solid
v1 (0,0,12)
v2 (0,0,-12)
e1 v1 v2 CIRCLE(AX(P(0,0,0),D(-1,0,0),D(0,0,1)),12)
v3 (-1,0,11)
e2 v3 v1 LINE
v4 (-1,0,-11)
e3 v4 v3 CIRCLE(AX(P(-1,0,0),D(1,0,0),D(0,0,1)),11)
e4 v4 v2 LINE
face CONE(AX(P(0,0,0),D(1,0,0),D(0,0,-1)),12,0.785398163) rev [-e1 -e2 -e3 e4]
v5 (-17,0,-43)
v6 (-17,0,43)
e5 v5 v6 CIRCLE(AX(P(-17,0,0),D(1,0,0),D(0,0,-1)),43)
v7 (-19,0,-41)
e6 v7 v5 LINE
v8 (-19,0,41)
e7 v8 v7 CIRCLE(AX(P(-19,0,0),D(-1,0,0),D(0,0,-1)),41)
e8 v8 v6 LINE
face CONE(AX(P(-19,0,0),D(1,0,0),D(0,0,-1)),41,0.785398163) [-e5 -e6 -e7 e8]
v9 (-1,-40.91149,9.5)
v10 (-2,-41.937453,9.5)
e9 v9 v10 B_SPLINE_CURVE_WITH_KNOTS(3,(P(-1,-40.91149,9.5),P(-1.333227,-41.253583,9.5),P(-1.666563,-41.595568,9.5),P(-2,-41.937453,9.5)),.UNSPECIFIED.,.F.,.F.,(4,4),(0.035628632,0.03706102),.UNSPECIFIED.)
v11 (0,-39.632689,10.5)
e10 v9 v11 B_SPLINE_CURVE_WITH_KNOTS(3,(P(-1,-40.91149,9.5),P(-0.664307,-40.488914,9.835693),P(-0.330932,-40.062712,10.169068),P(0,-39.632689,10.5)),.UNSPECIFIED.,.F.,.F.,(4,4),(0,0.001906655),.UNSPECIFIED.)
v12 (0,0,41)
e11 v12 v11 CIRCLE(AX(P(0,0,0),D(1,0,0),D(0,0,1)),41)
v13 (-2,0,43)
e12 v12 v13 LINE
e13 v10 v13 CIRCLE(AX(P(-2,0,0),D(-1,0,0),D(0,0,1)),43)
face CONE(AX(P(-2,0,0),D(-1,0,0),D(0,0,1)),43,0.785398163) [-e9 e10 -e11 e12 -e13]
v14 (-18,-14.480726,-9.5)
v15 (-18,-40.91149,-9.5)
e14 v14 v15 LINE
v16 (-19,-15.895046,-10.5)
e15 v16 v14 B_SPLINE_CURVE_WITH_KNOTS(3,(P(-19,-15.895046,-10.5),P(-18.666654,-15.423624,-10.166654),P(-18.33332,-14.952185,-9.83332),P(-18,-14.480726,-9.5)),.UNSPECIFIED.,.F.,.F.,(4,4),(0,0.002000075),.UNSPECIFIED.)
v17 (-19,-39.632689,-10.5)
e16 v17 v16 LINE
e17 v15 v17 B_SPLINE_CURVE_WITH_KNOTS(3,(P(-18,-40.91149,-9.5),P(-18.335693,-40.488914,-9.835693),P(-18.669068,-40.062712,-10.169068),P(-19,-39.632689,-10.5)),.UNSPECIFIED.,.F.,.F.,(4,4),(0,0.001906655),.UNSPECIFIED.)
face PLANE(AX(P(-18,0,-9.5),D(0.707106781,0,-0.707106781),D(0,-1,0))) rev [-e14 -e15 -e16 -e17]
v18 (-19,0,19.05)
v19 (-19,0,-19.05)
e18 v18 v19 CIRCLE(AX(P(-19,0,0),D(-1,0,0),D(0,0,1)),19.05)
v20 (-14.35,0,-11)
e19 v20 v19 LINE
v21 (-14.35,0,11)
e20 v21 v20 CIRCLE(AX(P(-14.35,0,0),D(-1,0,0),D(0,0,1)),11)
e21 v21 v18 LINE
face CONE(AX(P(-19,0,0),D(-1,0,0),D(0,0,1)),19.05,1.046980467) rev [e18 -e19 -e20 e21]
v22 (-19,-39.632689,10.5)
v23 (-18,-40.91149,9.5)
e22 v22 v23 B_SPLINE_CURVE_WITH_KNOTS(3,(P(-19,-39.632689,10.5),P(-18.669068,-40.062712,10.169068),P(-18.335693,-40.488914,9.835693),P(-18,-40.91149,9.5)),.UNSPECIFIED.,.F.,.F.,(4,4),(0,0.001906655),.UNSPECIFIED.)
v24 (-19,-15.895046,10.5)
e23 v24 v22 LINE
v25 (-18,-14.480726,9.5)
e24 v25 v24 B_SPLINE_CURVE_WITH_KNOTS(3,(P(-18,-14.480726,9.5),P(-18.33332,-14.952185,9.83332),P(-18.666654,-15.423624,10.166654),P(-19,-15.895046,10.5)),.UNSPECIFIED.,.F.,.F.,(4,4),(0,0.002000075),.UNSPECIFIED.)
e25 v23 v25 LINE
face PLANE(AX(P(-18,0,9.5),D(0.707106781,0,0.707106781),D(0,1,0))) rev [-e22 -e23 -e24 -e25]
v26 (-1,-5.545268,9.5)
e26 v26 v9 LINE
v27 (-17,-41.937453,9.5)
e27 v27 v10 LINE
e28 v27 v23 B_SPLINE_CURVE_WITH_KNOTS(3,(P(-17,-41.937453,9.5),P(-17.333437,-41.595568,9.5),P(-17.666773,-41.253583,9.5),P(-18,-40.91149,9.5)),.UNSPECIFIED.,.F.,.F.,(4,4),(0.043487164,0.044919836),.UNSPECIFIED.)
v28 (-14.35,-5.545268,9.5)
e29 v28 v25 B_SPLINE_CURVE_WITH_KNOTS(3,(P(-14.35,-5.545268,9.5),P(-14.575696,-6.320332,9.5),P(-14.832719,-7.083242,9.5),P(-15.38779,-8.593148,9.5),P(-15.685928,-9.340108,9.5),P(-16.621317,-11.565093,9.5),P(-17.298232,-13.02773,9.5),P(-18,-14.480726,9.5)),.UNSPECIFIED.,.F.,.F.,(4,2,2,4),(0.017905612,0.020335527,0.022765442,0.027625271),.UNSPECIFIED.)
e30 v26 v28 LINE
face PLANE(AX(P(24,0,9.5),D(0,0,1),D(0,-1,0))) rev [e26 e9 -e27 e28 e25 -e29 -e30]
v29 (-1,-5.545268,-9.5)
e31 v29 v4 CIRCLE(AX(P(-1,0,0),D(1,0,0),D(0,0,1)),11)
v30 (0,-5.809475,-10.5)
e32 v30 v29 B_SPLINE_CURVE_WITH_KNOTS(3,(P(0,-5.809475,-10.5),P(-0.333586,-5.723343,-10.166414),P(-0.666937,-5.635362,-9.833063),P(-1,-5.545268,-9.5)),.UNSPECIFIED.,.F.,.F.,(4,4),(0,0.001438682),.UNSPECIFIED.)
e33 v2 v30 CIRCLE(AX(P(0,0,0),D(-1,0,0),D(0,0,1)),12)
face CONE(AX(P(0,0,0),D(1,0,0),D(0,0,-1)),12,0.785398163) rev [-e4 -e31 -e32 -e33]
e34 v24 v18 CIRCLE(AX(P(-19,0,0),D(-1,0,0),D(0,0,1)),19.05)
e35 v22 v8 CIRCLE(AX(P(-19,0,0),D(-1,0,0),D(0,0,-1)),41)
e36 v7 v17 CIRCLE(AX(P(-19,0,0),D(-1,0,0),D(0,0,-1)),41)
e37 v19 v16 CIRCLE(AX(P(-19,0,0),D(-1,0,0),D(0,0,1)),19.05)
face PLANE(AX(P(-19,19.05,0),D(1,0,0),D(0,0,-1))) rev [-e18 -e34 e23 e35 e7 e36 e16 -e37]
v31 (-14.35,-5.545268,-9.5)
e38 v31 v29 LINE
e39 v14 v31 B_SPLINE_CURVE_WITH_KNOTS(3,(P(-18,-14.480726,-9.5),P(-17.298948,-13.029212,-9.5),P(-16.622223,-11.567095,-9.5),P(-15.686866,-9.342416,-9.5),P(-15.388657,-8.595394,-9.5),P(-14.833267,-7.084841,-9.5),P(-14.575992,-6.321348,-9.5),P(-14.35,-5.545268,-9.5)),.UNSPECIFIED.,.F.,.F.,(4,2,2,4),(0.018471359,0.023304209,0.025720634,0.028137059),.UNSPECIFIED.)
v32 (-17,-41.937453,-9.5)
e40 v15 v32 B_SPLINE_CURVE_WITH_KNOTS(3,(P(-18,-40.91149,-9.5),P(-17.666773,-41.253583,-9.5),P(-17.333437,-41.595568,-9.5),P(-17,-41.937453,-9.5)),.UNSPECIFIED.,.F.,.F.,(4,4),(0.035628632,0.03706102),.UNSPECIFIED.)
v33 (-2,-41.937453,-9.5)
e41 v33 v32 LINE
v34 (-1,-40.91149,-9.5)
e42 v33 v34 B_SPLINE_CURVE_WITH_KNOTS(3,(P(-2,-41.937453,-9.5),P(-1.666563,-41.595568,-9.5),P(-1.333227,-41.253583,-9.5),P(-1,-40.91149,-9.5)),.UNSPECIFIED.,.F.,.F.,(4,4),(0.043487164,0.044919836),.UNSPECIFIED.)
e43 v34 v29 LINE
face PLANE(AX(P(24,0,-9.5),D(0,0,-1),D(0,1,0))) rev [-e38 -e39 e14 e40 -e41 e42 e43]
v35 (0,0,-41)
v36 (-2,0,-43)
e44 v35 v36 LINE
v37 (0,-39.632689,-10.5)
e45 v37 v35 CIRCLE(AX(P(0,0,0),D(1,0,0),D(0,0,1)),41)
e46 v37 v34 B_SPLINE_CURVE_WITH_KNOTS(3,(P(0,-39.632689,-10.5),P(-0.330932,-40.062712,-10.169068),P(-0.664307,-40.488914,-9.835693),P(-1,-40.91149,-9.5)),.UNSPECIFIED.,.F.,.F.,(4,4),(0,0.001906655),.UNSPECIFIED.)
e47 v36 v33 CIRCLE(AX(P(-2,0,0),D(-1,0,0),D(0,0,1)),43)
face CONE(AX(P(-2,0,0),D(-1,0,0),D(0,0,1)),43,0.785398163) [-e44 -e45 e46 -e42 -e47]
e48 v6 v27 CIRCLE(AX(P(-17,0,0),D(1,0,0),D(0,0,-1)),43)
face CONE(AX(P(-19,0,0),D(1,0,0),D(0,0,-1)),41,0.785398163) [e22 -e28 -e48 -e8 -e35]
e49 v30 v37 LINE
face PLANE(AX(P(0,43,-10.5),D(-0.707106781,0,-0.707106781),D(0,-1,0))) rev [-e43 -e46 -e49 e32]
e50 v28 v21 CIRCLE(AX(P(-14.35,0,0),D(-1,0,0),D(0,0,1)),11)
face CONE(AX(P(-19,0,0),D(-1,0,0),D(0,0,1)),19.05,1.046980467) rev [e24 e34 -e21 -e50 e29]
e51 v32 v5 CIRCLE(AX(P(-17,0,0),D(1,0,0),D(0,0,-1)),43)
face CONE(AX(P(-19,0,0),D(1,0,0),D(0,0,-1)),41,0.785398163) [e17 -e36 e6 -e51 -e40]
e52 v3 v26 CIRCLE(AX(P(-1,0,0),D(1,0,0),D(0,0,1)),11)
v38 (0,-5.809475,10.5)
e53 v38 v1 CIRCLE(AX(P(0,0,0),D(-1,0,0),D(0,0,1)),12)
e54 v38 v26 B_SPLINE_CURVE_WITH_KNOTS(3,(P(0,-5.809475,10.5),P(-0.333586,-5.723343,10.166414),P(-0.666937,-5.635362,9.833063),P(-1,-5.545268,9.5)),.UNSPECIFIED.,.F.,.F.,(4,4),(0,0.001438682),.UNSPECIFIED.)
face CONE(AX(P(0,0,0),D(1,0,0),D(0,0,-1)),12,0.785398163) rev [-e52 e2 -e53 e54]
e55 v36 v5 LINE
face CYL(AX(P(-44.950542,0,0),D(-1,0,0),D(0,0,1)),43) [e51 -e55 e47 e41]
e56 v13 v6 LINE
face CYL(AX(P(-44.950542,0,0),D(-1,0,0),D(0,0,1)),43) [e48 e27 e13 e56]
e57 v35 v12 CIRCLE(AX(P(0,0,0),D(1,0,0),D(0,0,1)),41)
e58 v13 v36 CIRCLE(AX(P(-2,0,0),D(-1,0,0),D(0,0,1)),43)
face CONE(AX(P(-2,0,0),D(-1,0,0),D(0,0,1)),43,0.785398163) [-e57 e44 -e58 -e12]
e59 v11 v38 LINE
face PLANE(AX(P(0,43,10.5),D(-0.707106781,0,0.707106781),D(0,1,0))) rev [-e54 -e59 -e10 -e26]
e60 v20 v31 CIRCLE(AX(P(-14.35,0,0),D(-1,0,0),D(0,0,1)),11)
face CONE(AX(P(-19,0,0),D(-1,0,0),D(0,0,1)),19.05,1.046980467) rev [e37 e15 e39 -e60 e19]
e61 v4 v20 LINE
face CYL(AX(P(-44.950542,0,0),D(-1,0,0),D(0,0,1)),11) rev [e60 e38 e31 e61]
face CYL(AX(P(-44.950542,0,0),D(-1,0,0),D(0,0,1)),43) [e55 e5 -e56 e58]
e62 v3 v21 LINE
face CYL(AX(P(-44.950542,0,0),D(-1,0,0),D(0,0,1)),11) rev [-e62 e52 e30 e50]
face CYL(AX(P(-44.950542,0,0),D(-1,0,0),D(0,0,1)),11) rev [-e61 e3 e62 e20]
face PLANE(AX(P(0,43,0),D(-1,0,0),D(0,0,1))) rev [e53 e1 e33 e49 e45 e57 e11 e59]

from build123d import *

# Parameters (mm, degrees)
CHAMFER1_SIZE      = 2
CUT_EXTRUDE2_DEPTH = 43
CHAMFER2_SIZE      = 1


with BuildPart() as part:
    # Sketch1 → Revolve1 (revolve)
    with BuildSketch(Plane.XY, mode=Mode.PRIVATE) as revolve1_sk:
        Polygon((-19, 19.05), (-19, 43), (0, 43), (0, 11), (-14.35, 11), align=None)
    revolve(revolve1_sk.sketch.rotate(Axis((-44.950542037, 0, 0), (1, 0, 0)), 90), axis=Axis((-44.950542037, 0, 0), (1, 0, 0)))

    # Chamfer1
    chamfer1_edges = [part.edges().sort_by_distance(p)[0] for p in [
        (-19, 0, -43),
        (0, 0, -43),
    ]]
    chamfer(chamfer1_edges, length=CHAMFER1_SIZE)

    # Sketch13 → Cut-Extrude2 (cut)
    with BuildSketch(Plane.ZY.offset(19)):
        Polygon((-9.5, 0), (-9.5, -65.513992054), (9.5, -73.697131866), (9.5, 0), align=None)
    extrude(amount=-CUT_EXTRUDE2_DEPTH, mode=Mode.SUBTRACT)

    # Chamfer2
    chamfer2_edges = [part.edges().sort_by_distance(p)[0] for p in [
        (-19, -28.198199933, -9.5),
        (-19, -28.198199933, 9.5),
        (0, -22.714737827, -9.5),
        (0, 11, 0),
        (0, -22.714737827, 9.5),
    ]]
    chamfer(chamfer2_edges, length=CHAMFER2_SIZE)


solid = part.part
